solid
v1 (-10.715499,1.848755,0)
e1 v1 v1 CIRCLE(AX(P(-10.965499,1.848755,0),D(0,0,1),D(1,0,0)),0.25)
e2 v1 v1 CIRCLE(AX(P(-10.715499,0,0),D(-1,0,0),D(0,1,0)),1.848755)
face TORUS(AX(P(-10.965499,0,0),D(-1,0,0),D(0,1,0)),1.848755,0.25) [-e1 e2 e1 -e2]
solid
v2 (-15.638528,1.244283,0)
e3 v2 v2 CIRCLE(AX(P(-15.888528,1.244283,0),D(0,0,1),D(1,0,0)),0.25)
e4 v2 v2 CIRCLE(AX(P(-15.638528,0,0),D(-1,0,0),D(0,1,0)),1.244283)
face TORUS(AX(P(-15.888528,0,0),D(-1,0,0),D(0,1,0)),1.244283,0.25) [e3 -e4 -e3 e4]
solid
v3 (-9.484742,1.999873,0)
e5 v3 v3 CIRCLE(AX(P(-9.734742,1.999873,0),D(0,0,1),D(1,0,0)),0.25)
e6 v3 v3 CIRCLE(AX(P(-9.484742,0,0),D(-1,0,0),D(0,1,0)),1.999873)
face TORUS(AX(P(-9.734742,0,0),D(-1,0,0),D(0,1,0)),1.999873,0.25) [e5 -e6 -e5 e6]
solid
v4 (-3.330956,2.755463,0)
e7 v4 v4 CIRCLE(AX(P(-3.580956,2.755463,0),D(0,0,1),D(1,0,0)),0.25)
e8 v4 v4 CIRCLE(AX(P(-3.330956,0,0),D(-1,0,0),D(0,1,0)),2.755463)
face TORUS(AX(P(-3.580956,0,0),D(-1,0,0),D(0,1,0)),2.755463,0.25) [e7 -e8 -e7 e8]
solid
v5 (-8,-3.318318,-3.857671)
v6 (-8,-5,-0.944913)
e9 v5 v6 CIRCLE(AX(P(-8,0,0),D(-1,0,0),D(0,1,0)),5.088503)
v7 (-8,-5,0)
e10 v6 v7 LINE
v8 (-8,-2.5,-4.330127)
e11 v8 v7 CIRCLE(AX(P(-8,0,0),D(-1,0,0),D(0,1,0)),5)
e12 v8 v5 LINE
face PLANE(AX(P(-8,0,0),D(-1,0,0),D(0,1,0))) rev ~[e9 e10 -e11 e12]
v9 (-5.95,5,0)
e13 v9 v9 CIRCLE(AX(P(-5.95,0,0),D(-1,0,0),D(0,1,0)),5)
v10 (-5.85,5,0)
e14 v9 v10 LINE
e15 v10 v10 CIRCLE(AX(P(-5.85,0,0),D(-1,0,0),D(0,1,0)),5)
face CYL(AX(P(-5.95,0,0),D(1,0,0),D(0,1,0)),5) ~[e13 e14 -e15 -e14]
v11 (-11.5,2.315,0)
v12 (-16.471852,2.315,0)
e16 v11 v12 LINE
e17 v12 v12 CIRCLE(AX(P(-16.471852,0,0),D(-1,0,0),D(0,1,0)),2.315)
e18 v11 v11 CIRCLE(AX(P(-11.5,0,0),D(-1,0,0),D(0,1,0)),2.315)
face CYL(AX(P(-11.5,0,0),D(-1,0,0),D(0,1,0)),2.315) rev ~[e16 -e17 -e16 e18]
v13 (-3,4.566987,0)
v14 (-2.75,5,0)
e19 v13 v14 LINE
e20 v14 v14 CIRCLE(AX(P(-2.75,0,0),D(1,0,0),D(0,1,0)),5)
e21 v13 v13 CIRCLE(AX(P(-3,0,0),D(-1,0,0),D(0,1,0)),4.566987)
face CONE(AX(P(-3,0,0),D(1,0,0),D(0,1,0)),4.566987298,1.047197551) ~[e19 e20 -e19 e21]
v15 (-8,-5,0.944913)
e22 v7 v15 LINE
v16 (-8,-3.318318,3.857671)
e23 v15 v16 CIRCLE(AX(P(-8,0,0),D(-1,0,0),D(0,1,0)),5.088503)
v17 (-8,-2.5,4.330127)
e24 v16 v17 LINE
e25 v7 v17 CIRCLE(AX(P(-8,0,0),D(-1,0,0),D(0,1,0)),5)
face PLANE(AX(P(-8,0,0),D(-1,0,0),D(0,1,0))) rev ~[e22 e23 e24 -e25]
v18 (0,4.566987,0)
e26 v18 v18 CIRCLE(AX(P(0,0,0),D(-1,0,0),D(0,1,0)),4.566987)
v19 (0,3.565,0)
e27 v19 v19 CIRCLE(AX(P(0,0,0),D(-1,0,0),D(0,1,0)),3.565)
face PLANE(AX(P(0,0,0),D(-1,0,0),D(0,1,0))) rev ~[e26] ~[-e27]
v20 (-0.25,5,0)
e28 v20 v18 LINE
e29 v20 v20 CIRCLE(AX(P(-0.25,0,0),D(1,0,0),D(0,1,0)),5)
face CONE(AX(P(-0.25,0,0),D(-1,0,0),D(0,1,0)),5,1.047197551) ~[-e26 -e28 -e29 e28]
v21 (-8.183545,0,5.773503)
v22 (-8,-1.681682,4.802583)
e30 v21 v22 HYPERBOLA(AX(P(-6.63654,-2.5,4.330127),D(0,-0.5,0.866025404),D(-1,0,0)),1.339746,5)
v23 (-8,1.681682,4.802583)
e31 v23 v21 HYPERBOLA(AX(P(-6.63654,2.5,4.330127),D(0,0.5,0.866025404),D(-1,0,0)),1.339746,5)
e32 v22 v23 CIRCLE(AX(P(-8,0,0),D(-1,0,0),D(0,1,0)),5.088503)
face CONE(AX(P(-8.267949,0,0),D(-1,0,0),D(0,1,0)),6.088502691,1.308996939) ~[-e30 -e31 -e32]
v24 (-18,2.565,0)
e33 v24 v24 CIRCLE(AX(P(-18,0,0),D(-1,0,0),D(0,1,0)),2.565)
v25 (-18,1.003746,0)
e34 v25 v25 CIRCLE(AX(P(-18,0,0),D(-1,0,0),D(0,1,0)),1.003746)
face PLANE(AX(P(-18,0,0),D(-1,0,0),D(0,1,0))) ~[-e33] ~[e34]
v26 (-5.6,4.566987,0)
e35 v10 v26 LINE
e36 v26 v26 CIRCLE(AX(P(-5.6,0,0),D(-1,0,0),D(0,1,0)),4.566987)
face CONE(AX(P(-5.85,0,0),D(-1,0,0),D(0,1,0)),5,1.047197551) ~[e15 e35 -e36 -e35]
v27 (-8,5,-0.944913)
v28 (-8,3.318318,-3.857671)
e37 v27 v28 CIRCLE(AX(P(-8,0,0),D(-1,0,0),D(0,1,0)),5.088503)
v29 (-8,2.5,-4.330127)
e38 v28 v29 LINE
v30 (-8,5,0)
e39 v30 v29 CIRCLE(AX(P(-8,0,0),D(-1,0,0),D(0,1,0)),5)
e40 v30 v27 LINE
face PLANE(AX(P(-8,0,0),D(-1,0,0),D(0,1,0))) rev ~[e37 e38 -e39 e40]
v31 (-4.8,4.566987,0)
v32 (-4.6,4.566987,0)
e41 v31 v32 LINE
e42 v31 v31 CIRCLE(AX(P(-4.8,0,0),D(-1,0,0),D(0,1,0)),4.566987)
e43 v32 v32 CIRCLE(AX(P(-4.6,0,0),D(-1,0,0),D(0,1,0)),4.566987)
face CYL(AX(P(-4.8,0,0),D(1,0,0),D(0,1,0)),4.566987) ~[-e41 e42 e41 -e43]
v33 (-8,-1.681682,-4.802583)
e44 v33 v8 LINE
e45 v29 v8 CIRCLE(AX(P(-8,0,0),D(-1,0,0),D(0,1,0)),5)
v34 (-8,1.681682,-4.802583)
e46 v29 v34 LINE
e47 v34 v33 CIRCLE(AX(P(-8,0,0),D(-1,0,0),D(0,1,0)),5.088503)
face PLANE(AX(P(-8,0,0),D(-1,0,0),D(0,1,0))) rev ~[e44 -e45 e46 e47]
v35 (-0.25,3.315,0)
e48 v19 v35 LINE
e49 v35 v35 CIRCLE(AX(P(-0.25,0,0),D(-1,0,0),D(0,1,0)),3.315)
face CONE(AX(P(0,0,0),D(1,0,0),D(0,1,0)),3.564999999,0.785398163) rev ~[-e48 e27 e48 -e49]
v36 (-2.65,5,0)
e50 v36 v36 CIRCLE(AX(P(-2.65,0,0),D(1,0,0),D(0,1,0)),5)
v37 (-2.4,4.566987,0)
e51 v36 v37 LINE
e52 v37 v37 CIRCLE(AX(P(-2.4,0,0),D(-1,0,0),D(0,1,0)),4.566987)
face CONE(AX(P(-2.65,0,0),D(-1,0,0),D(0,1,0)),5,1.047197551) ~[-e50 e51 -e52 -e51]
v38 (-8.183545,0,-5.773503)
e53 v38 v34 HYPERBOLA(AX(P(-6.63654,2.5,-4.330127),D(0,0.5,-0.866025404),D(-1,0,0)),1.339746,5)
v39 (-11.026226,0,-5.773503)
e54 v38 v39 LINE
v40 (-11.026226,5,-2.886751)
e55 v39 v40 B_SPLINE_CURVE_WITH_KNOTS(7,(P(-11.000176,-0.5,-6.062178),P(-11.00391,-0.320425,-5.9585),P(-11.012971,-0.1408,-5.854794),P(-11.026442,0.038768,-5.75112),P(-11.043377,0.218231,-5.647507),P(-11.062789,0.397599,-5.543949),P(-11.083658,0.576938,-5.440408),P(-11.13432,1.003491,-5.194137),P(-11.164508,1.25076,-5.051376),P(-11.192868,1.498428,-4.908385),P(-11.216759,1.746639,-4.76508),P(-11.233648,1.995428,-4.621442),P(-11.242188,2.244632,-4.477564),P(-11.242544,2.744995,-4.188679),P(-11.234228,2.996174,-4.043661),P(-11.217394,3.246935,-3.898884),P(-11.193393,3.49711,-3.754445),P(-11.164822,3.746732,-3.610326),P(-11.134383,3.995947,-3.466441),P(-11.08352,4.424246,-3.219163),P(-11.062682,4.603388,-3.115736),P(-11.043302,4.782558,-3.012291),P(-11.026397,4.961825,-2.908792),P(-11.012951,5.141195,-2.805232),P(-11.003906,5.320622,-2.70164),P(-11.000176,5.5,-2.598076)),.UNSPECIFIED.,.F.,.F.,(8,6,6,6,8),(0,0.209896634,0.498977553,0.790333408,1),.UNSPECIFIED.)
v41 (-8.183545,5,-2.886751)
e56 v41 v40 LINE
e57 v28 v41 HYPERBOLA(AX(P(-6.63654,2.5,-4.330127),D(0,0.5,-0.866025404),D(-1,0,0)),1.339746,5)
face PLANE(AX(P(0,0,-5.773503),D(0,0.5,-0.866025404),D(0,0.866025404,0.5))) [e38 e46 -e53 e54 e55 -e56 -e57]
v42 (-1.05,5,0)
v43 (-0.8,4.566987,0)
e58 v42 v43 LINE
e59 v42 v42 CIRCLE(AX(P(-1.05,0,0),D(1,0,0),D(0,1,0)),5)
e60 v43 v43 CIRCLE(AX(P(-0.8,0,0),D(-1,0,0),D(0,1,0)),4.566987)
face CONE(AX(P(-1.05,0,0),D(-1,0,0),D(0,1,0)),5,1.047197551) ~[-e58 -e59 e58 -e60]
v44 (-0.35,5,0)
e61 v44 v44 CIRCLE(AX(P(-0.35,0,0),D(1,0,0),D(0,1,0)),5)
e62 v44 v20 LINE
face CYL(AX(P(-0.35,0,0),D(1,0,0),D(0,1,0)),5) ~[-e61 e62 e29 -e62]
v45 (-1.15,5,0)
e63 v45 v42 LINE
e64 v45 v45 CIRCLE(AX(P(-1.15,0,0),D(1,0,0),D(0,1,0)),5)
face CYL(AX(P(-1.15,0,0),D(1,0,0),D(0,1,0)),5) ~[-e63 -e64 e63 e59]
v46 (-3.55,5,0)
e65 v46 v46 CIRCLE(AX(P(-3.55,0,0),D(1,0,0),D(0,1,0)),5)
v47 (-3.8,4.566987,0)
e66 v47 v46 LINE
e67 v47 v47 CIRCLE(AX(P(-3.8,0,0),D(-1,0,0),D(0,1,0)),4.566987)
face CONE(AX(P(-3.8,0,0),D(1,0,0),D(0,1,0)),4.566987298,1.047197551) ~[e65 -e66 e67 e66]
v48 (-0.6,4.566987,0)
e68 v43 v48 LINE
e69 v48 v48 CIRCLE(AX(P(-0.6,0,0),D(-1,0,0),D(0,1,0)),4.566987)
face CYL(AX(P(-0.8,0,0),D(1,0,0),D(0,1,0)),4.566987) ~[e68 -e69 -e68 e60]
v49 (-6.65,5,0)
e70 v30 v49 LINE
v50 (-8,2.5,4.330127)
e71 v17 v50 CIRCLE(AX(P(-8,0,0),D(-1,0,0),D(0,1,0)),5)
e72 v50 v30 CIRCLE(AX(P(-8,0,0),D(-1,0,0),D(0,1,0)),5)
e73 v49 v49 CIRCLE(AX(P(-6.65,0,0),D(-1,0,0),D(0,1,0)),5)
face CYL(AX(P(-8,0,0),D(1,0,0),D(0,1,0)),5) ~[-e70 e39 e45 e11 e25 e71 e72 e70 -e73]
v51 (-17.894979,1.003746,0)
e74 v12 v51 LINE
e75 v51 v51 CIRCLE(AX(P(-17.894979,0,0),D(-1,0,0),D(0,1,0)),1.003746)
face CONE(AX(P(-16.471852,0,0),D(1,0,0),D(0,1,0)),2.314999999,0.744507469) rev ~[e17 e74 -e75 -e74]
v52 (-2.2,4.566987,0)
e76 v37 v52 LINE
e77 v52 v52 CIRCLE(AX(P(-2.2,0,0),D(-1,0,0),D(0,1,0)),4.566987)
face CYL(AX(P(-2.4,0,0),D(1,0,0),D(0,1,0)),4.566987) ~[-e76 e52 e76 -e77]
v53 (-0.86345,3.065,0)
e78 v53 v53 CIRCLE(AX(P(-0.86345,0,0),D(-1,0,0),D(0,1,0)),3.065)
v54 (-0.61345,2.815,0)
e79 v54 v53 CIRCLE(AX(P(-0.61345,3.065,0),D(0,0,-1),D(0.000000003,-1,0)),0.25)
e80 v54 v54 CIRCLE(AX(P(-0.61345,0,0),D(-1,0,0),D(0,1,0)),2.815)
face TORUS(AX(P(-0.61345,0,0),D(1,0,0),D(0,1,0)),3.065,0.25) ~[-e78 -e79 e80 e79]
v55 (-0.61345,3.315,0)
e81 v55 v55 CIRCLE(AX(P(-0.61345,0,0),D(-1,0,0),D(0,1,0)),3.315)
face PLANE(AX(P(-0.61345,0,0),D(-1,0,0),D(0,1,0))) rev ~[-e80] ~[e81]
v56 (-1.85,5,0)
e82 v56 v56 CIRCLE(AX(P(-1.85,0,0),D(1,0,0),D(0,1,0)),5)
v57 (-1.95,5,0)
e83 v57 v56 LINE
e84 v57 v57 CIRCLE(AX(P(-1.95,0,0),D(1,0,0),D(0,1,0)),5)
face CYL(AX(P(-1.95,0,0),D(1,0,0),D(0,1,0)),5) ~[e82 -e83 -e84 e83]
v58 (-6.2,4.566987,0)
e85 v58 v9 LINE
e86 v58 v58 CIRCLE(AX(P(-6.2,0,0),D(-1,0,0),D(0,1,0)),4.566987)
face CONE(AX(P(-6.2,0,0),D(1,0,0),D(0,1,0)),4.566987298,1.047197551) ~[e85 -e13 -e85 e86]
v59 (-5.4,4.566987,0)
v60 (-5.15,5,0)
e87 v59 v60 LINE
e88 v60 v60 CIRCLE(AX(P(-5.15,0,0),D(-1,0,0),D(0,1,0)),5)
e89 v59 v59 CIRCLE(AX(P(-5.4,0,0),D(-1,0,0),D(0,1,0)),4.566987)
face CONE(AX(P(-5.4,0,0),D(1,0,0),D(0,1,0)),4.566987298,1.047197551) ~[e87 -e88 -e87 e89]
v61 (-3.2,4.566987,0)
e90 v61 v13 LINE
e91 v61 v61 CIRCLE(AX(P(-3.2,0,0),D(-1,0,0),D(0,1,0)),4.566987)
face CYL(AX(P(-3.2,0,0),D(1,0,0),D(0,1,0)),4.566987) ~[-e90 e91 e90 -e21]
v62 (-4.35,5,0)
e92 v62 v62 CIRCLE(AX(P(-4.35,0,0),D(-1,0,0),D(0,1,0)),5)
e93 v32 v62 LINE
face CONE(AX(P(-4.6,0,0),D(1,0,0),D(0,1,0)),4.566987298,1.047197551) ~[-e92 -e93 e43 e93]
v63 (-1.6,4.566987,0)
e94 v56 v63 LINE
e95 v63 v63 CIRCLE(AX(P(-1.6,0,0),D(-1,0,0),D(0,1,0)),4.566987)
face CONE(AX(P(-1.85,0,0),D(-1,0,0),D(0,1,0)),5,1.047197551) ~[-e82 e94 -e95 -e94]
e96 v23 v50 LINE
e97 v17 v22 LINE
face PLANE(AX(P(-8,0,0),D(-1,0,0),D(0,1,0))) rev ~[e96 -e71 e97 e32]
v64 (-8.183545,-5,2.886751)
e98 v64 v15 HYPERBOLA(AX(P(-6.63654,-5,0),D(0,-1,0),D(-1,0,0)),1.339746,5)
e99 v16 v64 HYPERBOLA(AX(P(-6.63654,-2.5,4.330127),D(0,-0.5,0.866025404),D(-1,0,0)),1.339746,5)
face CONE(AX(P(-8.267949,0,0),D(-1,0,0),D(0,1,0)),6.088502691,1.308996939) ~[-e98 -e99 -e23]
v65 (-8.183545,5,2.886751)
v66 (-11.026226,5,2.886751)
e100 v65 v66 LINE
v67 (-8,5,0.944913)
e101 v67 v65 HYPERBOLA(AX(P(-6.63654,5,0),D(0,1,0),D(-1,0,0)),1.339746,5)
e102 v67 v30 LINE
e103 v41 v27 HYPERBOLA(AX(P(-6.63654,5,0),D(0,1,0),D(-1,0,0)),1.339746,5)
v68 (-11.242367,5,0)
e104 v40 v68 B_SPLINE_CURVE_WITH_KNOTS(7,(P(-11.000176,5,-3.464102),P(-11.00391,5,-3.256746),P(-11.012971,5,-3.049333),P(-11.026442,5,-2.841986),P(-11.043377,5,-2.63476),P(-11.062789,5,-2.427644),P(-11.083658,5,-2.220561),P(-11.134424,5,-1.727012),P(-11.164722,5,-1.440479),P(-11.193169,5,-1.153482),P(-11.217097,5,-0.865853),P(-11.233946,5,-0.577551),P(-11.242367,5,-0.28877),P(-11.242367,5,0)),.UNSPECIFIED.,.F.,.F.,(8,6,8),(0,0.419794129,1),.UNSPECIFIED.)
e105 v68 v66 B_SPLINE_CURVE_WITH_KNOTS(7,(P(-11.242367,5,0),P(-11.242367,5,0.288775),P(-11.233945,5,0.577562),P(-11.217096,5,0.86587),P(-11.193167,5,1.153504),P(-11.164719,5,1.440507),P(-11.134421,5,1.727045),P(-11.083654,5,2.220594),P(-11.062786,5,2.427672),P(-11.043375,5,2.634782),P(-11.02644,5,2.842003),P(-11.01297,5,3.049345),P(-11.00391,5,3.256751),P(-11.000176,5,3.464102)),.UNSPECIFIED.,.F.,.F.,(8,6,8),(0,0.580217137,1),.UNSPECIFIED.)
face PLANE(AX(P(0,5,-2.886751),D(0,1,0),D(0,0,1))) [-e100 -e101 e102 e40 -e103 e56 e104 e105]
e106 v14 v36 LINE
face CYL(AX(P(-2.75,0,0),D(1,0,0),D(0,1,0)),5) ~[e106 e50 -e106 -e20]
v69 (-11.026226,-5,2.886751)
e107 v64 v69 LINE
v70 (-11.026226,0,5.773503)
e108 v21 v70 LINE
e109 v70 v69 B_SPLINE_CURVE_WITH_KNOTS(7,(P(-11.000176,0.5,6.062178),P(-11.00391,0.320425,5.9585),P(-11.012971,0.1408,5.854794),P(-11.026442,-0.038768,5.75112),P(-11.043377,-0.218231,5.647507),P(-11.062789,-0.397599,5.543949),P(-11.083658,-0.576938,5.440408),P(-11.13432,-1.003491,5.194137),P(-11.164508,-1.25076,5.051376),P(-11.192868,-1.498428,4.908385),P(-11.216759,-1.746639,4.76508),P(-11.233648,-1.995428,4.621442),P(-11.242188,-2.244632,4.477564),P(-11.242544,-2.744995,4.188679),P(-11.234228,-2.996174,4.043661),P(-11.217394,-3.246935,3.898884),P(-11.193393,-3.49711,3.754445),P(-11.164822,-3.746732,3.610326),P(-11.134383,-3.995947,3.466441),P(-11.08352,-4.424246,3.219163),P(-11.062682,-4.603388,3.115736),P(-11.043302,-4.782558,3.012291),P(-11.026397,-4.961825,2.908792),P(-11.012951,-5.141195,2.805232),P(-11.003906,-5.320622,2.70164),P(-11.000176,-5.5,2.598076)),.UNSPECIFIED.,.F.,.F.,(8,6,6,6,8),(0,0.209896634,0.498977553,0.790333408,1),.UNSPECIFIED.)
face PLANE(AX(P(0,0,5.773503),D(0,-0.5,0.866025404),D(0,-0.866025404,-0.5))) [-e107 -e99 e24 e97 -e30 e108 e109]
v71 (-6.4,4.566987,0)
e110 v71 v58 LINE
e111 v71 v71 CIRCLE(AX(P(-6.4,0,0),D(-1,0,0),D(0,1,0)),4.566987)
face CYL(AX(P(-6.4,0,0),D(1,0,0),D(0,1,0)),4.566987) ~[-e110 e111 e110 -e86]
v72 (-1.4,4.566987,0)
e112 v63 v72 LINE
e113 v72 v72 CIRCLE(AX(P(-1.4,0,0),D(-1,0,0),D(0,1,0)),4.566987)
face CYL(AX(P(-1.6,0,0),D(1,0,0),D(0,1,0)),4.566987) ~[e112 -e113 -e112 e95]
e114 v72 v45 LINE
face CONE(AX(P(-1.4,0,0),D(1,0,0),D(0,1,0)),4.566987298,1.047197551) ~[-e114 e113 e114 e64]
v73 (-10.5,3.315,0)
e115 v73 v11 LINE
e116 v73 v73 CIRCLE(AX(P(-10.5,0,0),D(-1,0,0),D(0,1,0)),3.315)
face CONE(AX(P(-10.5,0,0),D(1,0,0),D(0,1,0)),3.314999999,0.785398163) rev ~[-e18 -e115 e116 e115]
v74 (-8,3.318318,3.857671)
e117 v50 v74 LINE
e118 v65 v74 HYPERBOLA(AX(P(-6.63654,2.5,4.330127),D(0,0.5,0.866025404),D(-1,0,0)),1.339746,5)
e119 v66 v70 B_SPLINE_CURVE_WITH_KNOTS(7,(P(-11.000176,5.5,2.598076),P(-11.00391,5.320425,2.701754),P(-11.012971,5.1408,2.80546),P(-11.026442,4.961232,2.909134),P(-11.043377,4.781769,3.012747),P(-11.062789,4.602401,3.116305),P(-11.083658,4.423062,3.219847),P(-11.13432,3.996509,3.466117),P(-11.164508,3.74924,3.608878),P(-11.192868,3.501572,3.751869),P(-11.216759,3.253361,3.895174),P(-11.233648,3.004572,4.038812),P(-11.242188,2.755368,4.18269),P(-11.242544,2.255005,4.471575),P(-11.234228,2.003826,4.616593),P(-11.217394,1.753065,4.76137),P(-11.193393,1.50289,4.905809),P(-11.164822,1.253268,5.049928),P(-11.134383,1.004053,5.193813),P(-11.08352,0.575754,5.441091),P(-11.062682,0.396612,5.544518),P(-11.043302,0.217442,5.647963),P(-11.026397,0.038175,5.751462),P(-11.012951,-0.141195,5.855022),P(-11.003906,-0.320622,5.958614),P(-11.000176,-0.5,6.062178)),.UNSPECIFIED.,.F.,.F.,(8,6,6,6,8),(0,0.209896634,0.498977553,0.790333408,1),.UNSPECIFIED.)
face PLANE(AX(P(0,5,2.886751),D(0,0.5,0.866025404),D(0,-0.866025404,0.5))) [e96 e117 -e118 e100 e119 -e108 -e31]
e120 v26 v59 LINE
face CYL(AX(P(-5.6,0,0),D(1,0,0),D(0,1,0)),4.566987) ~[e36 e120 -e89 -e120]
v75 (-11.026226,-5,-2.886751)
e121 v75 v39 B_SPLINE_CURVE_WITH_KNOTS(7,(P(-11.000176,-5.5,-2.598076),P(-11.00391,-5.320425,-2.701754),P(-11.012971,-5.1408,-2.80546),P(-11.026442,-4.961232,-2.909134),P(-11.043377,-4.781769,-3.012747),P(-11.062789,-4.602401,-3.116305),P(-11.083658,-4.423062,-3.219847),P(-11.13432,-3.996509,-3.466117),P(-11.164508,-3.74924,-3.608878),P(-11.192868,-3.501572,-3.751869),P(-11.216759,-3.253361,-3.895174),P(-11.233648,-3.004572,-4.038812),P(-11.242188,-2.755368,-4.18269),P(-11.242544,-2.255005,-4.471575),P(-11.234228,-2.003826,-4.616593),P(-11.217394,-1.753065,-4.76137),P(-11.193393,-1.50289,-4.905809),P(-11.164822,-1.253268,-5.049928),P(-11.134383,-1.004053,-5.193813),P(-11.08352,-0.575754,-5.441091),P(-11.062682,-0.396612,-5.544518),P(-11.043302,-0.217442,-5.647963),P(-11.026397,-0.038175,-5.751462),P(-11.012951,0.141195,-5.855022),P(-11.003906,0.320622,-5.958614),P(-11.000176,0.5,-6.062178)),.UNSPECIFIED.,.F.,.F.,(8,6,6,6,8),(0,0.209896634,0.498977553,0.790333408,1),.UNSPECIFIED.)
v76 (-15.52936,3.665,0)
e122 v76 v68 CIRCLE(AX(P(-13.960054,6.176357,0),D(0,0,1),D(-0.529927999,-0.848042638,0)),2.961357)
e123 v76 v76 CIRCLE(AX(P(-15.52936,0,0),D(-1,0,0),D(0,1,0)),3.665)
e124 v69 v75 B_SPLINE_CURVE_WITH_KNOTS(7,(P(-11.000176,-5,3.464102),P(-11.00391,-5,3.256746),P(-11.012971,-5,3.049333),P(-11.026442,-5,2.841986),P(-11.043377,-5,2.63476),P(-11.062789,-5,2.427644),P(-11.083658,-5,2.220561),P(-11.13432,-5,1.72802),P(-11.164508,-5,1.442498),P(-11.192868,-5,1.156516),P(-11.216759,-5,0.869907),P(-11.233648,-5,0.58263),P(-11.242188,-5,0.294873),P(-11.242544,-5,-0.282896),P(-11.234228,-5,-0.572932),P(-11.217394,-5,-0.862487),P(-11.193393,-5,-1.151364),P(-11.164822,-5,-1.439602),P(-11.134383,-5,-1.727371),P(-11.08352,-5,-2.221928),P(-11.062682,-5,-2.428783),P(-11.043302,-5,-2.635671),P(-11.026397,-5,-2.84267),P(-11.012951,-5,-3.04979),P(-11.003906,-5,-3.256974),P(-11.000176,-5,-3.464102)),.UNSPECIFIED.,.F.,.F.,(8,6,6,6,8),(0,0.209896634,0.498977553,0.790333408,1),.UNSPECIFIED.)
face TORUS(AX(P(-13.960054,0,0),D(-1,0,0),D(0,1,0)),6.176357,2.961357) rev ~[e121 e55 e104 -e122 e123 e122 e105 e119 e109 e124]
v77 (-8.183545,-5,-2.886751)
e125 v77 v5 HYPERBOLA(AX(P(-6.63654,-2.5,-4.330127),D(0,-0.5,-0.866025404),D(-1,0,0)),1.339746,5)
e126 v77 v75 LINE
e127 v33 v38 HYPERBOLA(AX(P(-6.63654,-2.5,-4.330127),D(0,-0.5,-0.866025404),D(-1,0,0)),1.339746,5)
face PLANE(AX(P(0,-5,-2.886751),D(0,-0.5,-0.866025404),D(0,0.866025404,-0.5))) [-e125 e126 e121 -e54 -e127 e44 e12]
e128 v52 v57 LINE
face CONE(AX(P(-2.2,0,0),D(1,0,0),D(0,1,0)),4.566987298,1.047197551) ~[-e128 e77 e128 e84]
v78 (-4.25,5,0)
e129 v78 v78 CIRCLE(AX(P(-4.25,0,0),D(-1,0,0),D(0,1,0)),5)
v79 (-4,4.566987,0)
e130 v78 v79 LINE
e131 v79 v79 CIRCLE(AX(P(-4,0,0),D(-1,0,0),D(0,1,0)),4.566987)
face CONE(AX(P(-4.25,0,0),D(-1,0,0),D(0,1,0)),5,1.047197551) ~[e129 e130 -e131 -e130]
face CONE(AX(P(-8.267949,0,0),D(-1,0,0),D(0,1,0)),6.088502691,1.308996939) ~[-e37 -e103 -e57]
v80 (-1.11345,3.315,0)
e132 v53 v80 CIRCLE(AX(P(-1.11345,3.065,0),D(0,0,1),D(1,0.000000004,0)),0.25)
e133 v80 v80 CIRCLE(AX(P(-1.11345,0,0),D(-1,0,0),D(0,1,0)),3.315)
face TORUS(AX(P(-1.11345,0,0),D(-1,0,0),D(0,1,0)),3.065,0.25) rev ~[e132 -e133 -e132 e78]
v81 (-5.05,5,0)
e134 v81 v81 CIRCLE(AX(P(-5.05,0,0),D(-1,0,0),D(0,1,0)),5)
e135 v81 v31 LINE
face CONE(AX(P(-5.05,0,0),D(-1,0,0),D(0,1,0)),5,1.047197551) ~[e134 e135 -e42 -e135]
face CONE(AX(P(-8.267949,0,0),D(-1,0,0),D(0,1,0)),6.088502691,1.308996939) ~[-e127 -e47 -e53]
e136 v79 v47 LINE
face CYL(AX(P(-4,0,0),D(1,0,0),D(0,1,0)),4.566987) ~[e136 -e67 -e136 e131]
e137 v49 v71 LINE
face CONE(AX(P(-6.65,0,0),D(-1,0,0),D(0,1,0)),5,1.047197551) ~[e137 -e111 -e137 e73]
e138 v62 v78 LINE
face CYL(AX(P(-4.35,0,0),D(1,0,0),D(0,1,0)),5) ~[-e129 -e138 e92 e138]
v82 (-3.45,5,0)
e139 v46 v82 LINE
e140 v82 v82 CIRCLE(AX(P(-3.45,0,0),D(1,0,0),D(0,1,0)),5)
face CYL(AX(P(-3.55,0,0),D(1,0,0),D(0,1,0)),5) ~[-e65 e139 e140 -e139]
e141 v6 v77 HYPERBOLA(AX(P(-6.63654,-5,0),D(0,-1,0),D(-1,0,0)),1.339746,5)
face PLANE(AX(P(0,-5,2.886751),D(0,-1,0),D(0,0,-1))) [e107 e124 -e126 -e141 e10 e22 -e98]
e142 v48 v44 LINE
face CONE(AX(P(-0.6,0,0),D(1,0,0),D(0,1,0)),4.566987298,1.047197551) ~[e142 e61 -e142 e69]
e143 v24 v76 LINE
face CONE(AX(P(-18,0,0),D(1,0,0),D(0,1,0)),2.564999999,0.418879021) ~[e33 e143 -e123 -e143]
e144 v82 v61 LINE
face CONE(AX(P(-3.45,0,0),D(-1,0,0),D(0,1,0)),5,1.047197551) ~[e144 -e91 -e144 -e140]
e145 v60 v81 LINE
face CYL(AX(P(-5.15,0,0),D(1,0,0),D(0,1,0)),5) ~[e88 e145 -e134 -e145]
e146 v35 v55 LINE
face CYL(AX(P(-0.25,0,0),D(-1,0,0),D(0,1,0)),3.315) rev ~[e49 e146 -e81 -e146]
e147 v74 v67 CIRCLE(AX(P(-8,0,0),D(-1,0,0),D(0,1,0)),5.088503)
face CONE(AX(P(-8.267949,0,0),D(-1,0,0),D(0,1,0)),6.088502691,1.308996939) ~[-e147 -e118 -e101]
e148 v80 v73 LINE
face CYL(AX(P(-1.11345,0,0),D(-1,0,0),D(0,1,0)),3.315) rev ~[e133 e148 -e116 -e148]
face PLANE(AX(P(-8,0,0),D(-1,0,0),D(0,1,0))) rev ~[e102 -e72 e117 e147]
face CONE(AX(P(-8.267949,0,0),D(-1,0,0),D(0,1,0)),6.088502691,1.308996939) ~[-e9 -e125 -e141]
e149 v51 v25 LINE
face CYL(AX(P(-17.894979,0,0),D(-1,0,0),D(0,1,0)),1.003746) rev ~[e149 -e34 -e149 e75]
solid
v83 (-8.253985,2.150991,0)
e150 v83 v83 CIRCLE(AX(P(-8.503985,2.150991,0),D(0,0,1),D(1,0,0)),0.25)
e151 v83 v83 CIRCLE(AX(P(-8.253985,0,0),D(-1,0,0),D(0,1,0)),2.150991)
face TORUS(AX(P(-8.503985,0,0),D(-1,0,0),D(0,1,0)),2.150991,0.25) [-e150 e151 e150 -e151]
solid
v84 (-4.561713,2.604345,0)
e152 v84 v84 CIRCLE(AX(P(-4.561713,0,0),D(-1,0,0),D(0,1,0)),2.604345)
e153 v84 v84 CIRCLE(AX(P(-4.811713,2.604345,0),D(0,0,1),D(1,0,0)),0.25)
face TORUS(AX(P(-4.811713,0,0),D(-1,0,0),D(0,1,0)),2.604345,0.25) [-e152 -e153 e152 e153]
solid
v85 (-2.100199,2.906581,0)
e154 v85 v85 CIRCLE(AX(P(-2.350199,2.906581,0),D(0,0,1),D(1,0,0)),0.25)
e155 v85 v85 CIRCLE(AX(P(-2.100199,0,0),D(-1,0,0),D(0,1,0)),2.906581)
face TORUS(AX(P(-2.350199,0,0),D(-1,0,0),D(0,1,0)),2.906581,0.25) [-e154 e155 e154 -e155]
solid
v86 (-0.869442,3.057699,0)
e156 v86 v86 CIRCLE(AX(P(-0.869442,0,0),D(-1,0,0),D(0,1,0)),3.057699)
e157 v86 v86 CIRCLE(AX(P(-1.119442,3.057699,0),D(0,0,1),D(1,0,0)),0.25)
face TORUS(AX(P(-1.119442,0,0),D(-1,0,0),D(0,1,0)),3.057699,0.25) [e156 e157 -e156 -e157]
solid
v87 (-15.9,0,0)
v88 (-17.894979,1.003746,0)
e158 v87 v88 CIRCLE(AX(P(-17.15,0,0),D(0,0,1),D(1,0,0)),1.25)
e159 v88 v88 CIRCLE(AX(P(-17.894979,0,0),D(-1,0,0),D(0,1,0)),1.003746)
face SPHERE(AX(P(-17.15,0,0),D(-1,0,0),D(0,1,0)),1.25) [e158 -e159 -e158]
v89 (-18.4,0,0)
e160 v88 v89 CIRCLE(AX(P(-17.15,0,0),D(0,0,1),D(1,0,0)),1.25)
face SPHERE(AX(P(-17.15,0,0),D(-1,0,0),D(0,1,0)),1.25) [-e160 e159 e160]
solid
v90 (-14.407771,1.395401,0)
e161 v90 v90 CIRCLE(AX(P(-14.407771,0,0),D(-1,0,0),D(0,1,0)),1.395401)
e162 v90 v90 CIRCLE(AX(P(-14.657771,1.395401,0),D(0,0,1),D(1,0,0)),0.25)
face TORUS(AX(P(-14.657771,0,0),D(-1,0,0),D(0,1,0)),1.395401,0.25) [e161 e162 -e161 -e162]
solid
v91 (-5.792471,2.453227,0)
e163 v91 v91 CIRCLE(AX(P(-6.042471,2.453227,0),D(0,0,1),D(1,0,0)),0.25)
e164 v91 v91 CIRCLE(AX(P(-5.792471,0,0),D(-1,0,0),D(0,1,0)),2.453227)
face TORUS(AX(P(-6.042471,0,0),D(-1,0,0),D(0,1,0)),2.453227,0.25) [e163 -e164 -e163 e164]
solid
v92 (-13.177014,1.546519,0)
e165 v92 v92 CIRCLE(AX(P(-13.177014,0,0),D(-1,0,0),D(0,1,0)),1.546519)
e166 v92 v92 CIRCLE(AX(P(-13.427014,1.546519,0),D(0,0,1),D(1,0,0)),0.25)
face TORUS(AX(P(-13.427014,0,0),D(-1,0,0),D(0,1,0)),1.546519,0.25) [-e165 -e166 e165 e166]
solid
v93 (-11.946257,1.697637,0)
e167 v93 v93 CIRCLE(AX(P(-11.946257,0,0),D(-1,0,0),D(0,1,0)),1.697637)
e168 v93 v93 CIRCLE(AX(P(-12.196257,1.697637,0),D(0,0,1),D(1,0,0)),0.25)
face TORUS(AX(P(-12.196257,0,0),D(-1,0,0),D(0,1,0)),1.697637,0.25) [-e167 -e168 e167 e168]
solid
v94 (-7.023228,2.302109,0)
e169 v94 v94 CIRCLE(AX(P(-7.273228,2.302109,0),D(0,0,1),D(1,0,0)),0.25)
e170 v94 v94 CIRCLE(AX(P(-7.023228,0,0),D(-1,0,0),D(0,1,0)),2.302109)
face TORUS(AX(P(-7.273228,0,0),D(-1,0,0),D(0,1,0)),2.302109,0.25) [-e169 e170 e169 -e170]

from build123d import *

# Parameters (mm, degrees)
SKETCH_1_R          = 0.25
SKETCH_2_R          = 10.539140362
CUT_EXTRUDE_1_DEPTH = 21.31501243


with BuildPart() as part:
    # 草图1 → 旋转1 (revolve)
    with BuildSketch(Plane.XY):
        with BuildLine():
            Line((-1.11345007, 3.314999999), (-10.5, 3.314999999))
            Line((-10.5, 3.314999999), (-11.5, 2.314999999))
            Line((-11.5, 2.314999999), (-16.471851993, 2.314999999))
            Line((-16.471851993, 2.314999999), (-17.89497877, 1.003746299))
            Line((-17.89497877, 1.003746299), (-18, 1.003746299))
            Line((-18, 1.003746299), (-18, 2.564999999))
            Line((-18, 2.564999999), (-15.529359549, 3.664999999))
            ThreePointArc((-15.529359549, 3.664999999), (-12.562954408, 3.565274985), (-11, 6.088502691))
            Line((-11, 6.088502691), (-8.267949192, 6.088502691))
            Line((-8.267949192, 6.088502691), (-8, 5.088502691))
            Line((-8, 5.088502691), (-8, 5))
            Line((-8, 5), (-6.65, 5))
            Line((-6.65, 5), (-6.4, 4.566987298))
            Line((-6.4, 4.566987298), (-6.2, 4.566987298))
            Line((-6.2, 4.566987298), (-5.95, 5))
            Line((-5.95, 5), (-5.85, 5))
            Line((-5.85, 5), (-5.6, 4.566987298))
            Line((-5.6, 4.566987298), (-5.4, 4.566987298))
            Line((-5.4, 4.566987298), (-5.15, 5))
            Line((-5.15, 5), (-5.05, 5))
            Line((-5.05, 5), (-4.8, 4.566987298))
            Line((-4.8, 4.566987298), (-4.6, 4.566987298))
            Line((-4.6, 4.566987298), (-4.35, 5))
            Line((-4.35, 5), (-4.25, 5))
            Line((-4.25, 5), (-4, 4.566987298))
            Line((-4, 4.566987298), (-3.8, 4.566987298))
            Line((-3.8, 4.566987298), (-3.55, 5))
            Line((-3.55, 5), (-3.45, 5))
            Line((-3.45, 5), (-3.2, 4.566987298))
            Line((-3.2, 4.566987298), (-3, 4.566987298))
            Line((-3, 4.566987298), (-2.75, 5))
            Line((-2.75, 5), (-2.65, 5))
            Line((-2.65, 5), (-2.4, 4.566987298))
            Line((-2.4, 4.566987298), (-2.2, 4.566987298))
            Line((-2.2, 4.566987298), (-1.95, 5))
            Line((-1.95, 5), (-1.85, 5))
            Line((-1.85, 5), (-1.6, 4.566987298))
            Line((-1.6, 4.566987298), (-1.4, 4.566987298))
            Line((-1.4, 4.566987298), (-1.15, 5))
            Line((-1.15, 5), (-1.05, 5))
            Line((-1.05, 5), (-0.8, 4.566987298))
            Line((-0.8, 4.566987298), (-0.6, 4.566987298))
            Line((-0.6, 4.566987298), (-0.35, 5))
            Line((-0.35, 5), (-0.25, 5))
            Line((-0.25, 5), (0, 4.566987298))
            Line((0, 4.566987298), (0, 3.564999999))
            Line((0, 3.564999999), (-0.25, 3.314999999))
            Line((-0.25, 3.314999999), (-0.61345007, 3.314999999))
            Line((-0.61345007, 3.314999999), (-0.61345007, 2.814999999))
            ThreePointArc((-0.61345007, 2.814999999), (-0.790226765, 2.888223303), (-0.86345007, 3.064999999))
            ThreePointArc((-0.86345007, 3.064999999), (-0.936673375, 3.241776694), (-1.11345007, 3.314999999))
        make_face()
        with BuildLine():
            ThreePointArc((-15.9, 0), (-17.15, 1.25), (-18.4, 0))
            Line((-18.4, 0), (-15.9, 0))
        make_face()
        with Locations((-15.888528375, 1.244283066)):
            Circle(SKETCH_1_R)
        with Locations((-14.657771147, 1.395401052)):
            Circle(SKETCH_1_R)
        with Locations((-13.427013919, 1.546519038)):
            Circle(SKETCH_1_R)
        with Locations((-12.19625669, 1.697637024)):
            Circle(SKETCH_1_R)
        with Locations((-10.965499462, 1.84875501)):
            Circle(SKETCH_1_R)
        with Locations((-9.734742234, 1.999872995)):
            Circle(SKETCH_1_R)
        with Locations((-8.503985006, 2.150990981)):
            Circle(SKETCH_1_R)
        with Locations((-7.273227778, 2.302108967)):
            Circle(SKETCH_1_R)
        with Locations((-6.04247055, 2.453226953)):
            Circle(SKETCH_1_R)
        with Locations((-4.811713322, 2.604344939)):
            Circle(SKETCH_1_R)
        with Locations((-3.580956094, 2.755462925)):
            Circle(SKETCH_1_R)
        with Locations((-2.350198866, 2.90658091)):
            Circle(SKETCH_1_R)
        with Locations((-1.119441638, 3.057698896)):
            Circle(SKETCH_1_R)
    revolve(axis=Axis((0, 0, 0), (-1, 0, 0)))

    # 草图2 → 切除-拉伸1 (cut, through all)
    with BuildSketch(Plane(origin=(0, 0, 0), x_dir=(0, 0, -1), z_dir=(1, 0, 0))):
        Circle(SKETCH_2_R)
        Polygon((5.773502692, 0), (2.886751346, 5), (-2.886751346, 5), (-5.773502692, 0), (-2.886751346, -5), (2.886751346, -5), align=None, mode=Mode.SUBTRACT)
    extrude(amount=-CUT_EXTRUDE_1_DEPTH, mode=Mode.SUBTRACT)


solid = part.part
